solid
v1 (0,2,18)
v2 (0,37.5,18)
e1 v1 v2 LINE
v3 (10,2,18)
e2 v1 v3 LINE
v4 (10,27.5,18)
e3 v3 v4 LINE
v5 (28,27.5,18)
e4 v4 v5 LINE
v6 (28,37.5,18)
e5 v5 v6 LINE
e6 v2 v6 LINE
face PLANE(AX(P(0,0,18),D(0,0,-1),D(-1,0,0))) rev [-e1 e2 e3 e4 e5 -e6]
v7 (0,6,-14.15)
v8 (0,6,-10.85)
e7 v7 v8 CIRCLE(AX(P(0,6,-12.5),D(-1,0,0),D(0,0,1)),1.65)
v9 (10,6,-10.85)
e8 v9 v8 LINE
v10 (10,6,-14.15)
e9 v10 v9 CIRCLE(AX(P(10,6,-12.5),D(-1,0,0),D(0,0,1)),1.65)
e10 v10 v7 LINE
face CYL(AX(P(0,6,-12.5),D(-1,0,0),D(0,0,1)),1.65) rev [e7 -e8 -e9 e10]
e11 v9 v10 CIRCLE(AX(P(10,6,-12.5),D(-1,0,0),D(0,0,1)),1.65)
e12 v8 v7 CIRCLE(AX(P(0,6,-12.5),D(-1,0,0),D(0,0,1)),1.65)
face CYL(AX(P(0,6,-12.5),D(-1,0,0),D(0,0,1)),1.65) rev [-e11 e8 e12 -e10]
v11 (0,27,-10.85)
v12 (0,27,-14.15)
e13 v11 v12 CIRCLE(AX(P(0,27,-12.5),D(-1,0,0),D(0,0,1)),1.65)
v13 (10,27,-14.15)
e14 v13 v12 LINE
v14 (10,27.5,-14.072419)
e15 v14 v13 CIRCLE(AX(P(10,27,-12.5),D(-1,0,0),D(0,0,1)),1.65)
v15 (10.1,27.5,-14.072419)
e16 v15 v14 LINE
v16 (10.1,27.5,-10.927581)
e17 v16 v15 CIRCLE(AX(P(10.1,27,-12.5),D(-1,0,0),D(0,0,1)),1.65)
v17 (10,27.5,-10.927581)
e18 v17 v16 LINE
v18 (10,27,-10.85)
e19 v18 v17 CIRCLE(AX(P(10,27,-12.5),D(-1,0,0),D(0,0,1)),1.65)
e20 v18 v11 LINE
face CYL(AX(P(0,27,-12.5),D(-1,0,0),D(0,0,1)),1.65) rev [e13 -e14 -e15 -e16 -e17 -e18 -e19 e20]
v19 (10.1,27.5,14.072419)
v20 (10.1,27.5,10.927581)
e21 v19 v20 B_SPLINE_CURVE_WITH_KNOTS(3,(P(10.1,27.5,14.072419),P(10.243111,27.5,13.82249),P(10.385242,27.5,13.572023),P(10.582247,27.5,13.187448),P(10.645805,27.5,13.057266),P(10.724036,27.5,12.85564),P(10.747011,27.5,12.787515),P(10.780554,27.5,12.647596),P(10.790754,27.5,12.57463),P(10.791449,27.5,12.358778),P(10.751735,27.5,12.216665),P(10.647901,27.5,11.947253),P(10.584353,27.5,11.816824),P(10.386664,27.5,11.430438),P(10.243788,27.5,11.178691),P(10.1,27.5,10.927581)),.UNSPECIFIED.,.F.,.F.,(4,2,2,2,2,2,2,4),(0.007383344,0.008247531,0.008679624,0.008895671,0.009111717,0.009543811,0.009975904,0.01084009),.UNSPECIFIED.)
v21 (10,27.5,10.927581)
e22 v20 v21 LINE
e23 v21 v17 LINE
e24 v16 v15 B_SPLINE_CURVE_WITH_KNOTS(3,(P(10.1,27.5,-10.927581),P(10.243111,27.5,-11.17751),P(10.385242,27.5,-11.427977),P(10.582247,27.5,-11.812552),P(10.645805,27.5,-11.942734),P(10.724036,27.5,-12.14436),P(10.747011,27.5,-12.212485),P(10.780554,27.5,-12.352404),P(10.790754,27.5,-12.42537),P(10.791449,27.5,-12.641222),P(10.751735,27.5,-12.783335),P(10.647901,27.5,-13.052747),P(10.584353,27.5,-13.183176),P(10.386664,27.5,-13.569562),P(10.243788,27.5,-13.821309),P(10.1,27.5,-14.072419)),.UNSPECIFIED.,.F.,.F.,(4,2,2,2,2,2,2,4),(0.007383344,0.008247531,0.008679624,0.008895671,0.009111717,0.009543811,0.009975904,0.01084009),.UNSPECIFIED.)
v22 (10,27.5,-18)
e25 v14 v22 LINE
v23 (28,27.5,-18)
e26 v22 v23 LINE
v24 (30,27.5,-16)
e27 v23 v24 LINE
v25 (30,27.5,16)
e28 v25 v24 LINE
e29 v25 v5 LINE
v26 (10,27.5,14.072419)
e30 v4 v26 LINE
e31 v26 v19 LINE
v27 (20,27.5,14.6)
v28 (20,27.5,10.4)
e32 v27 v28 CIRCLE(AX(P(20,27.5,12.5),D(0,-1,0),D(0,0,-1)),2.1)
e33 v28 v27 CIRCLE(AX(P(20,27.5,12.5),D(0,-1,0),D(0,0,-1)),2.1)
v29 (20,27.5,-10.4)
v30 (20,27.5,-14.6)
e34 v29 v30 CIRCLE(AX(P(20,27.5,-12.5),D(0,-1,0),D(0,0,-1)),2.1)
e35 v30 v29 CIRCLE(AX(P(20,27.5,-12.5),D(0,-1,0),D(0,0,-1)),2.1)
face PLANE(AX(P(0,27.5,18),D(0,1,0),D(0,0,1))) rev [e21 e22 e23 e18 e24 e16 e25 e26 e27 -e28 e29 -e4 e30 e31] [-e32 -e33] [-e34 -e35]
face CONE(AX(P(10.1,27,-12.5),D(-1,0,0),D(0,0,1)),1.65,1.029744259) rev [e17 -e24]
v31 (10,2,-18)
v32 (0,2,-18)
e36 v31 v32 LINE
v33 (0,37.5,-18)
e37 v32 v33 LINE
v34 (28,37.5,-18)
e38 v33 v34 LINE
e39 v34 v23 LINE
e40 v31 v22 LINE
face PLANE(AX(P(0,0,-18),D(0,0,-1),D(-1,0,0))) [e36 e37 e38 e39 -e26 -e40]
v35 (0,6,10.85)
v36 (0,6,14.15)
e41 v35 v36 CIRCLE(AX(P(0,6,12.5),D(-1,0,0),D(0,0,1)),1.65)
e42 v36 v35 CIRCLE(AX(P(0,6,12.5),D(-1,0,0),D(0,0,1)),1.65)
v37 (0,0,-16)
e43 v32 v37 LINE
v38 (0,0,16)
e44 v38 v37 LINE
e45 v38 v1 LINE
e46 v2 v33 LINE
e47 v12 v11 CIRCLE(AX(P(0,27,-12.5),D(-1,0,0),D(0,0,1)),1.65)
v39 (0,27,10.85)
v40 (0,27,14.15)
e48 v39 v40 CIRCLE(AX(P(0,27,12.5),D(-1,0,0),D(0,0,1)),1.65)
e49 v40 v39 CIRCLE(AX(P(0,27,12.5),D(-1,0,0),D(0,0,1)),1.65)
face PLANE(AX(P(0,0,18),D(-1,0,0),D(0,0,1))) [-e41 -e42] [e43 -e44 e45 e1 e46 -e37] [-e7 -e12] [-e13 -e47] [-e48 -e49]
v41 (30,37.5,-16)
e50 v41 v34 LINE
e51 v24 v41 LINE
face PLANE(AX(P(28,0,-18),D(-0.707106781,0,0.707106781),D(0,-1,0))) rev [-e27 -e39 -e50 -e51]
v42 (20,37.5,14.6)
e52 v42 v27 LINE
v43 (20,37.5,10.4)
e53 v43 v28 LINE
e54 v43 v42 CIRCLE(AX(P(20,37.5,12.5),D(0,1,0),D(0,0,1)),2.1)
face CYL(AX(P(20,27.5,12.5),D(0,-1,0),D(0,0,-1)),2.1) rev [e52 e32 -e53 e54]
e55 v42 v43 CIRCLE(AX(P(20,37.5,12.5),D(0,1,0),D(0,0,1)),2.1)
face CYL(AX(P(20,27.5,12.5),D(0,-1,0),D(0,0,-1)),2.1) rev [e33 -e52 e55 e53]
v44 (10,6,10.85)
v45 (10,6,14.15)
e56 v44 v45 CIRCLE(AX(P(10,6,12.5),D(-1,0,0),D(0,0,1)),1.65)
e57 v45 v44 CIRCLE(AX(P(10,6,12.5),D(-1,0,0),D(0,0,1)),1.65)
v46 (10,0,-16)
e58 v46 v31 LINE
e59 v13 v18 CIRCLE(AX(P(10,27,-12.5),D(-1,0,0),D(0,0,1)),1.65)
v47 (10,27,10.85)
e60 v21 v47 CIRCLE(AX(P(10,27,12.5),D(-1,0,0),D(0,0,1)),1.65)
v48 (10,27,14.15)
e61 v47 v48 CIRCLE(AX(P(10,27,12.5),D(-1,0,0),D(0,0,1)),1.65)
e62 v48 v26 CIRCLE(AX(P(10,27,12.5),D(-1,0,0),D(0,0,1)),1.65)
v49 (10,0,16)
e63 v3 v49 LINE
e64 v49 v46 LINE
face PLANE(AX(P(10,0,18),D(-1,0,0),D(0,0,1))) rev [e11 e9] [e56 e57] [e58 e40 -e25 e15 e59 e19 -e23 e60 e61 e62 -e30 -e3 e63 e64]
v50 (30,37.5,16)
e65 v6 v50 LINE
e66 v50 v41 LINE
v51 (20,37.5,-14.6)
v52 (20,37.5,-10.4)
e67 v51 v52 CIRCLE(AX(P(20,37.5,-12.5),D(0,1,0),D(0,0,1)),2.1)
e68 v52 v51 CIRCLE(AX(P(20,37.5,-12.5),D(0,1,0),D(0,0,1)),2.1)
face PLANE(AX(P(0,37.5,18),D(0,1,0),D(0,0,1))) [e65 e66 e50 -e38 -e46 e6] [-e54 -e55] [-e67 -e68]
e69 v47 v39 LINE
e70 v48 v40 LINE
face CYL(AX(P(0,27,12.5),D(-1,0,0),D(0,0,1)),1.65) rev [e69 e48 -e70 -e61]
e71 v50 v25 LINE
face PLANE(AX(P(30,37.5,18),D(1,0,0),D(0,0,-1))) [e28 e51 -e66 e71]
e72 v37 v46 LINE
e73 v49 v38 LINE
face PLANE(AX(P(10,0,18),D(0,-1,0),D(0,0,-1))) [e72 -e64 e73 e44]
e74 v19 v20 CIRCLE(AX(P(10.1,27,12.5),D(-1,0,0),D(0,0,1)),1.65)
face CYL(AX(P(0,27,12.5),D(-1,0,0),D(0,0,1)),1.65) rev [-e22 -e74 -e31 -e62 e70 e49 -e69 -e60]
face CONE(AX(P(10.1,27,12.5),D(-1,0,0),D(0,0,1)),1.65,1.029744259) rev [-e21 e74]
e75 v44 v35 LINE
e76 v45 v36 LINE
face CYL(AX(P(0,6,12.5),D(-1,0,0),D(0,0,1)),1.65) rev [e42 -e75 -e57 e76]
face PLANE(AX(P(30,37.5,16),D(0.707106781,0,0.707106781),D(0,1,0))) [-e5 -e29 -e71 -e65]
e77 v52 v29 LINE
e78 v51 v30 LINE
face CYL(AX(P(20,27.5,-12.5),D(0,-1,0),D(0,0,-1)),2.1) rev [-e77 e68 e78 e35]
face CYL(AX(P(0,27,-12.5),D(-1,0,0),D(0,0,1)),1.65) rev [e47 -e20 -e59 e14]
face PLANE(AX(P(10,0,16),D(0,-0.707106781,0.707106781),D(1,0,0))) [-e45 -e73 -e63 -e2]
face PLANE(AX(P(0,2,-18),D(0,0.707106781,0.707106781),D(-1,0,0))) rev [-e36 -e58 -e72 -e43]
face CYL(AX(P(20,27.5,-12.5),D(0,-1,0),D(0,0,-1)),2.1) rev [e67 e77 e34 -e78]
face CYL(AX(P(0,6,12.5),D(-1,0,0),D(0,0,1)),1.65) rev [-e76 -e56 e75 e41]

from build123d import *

# Parameters (mm, degrees)
EXTRUDE_1_DEPTH        = 18
CHAMFER_1_SIZE         = 2
HOLE_WIZARD_M4_1_D     = 3.3
HOLE_WIZARD_M4_1_DEPTH = 10.1
HOLE_WIZARD_M4_1_TIP   = 0.991420021
HOLE_WIZARD_M5_1_D     = 4.2
HOLE_WIZARD_M5_1_DEPTH = 12.4
HOLE_WIZARD_M5_1_TIP   = 1.2618073


with BuildPart() as part:
    # 草图1 → 拉伸-薄壁1 (new, symmetric)
    with BuildSketch(Plane.XY):
        Polygon((0, 0), (0, 37.5), (30, 37.5), (30, 27.5), (10, 27.5), (10, 0), align=None)
    extrude(amount=EXTRUDE_1_DEPTH, both=True)

    # 倒角1
    chamfer_1_edges = [part.edges().sort_by_distance(p)[0] for p in [
        (5, 0, 18),
        (5, 0, -18),
        (30, 32.5, -18),
        (30, 32.5, 18),
    ]]
    chamfer(chamfer_1_edges, length=CHAMFER_1_SIZE)

    # M4 螺纹孔1
    with Locations(Plane.ZY):
        with Locations((12.5, 27), (12.5, 6), (-12.5, 6), (-12.5, 27)):
            Hole(HOLE_WIZARD_M4_1_D / 2, depth=HOLE_WIZARD_M4_1_DEPTH)
            with Locations((0, 0, -(HOLE_WIZARD_M4_1_DEPTH + HOLE_WIZARD_M4_1_TIP / 2))):  # 118° drill point
                Cone(0, HOLE_WIZARD_M4_1_D / 2, HOLE_WIZARD_M4_1_TIP, mode=Mode.SUBTRACT)

    # M5 螺纹孔1
    with Locations(Plane(origin=(0, 27.5, 0), x_dir=(-1, 0, 0), z_dir=(0, -1, 0))):
        with Locations((-20, 12.5), (-20, -12.5)):
            Hole(HOLE_WIZARD_M5_1_D / 2, depth=HOLE_WIZARD_M5_1_DEPTH)
            with Locations((0, 0, -(HOLE_WIZARD_M5_1_DEPTH + HOLE_WIZARD_M5_1_TIP / 2))):  # 118° drill point
                Cone(0, HOLE_WIZARD_M5_1_D / 2, HOLE_WIZARD_M5_1_TIP, mode=Mode.SUBTRACT)


solid = part.part
